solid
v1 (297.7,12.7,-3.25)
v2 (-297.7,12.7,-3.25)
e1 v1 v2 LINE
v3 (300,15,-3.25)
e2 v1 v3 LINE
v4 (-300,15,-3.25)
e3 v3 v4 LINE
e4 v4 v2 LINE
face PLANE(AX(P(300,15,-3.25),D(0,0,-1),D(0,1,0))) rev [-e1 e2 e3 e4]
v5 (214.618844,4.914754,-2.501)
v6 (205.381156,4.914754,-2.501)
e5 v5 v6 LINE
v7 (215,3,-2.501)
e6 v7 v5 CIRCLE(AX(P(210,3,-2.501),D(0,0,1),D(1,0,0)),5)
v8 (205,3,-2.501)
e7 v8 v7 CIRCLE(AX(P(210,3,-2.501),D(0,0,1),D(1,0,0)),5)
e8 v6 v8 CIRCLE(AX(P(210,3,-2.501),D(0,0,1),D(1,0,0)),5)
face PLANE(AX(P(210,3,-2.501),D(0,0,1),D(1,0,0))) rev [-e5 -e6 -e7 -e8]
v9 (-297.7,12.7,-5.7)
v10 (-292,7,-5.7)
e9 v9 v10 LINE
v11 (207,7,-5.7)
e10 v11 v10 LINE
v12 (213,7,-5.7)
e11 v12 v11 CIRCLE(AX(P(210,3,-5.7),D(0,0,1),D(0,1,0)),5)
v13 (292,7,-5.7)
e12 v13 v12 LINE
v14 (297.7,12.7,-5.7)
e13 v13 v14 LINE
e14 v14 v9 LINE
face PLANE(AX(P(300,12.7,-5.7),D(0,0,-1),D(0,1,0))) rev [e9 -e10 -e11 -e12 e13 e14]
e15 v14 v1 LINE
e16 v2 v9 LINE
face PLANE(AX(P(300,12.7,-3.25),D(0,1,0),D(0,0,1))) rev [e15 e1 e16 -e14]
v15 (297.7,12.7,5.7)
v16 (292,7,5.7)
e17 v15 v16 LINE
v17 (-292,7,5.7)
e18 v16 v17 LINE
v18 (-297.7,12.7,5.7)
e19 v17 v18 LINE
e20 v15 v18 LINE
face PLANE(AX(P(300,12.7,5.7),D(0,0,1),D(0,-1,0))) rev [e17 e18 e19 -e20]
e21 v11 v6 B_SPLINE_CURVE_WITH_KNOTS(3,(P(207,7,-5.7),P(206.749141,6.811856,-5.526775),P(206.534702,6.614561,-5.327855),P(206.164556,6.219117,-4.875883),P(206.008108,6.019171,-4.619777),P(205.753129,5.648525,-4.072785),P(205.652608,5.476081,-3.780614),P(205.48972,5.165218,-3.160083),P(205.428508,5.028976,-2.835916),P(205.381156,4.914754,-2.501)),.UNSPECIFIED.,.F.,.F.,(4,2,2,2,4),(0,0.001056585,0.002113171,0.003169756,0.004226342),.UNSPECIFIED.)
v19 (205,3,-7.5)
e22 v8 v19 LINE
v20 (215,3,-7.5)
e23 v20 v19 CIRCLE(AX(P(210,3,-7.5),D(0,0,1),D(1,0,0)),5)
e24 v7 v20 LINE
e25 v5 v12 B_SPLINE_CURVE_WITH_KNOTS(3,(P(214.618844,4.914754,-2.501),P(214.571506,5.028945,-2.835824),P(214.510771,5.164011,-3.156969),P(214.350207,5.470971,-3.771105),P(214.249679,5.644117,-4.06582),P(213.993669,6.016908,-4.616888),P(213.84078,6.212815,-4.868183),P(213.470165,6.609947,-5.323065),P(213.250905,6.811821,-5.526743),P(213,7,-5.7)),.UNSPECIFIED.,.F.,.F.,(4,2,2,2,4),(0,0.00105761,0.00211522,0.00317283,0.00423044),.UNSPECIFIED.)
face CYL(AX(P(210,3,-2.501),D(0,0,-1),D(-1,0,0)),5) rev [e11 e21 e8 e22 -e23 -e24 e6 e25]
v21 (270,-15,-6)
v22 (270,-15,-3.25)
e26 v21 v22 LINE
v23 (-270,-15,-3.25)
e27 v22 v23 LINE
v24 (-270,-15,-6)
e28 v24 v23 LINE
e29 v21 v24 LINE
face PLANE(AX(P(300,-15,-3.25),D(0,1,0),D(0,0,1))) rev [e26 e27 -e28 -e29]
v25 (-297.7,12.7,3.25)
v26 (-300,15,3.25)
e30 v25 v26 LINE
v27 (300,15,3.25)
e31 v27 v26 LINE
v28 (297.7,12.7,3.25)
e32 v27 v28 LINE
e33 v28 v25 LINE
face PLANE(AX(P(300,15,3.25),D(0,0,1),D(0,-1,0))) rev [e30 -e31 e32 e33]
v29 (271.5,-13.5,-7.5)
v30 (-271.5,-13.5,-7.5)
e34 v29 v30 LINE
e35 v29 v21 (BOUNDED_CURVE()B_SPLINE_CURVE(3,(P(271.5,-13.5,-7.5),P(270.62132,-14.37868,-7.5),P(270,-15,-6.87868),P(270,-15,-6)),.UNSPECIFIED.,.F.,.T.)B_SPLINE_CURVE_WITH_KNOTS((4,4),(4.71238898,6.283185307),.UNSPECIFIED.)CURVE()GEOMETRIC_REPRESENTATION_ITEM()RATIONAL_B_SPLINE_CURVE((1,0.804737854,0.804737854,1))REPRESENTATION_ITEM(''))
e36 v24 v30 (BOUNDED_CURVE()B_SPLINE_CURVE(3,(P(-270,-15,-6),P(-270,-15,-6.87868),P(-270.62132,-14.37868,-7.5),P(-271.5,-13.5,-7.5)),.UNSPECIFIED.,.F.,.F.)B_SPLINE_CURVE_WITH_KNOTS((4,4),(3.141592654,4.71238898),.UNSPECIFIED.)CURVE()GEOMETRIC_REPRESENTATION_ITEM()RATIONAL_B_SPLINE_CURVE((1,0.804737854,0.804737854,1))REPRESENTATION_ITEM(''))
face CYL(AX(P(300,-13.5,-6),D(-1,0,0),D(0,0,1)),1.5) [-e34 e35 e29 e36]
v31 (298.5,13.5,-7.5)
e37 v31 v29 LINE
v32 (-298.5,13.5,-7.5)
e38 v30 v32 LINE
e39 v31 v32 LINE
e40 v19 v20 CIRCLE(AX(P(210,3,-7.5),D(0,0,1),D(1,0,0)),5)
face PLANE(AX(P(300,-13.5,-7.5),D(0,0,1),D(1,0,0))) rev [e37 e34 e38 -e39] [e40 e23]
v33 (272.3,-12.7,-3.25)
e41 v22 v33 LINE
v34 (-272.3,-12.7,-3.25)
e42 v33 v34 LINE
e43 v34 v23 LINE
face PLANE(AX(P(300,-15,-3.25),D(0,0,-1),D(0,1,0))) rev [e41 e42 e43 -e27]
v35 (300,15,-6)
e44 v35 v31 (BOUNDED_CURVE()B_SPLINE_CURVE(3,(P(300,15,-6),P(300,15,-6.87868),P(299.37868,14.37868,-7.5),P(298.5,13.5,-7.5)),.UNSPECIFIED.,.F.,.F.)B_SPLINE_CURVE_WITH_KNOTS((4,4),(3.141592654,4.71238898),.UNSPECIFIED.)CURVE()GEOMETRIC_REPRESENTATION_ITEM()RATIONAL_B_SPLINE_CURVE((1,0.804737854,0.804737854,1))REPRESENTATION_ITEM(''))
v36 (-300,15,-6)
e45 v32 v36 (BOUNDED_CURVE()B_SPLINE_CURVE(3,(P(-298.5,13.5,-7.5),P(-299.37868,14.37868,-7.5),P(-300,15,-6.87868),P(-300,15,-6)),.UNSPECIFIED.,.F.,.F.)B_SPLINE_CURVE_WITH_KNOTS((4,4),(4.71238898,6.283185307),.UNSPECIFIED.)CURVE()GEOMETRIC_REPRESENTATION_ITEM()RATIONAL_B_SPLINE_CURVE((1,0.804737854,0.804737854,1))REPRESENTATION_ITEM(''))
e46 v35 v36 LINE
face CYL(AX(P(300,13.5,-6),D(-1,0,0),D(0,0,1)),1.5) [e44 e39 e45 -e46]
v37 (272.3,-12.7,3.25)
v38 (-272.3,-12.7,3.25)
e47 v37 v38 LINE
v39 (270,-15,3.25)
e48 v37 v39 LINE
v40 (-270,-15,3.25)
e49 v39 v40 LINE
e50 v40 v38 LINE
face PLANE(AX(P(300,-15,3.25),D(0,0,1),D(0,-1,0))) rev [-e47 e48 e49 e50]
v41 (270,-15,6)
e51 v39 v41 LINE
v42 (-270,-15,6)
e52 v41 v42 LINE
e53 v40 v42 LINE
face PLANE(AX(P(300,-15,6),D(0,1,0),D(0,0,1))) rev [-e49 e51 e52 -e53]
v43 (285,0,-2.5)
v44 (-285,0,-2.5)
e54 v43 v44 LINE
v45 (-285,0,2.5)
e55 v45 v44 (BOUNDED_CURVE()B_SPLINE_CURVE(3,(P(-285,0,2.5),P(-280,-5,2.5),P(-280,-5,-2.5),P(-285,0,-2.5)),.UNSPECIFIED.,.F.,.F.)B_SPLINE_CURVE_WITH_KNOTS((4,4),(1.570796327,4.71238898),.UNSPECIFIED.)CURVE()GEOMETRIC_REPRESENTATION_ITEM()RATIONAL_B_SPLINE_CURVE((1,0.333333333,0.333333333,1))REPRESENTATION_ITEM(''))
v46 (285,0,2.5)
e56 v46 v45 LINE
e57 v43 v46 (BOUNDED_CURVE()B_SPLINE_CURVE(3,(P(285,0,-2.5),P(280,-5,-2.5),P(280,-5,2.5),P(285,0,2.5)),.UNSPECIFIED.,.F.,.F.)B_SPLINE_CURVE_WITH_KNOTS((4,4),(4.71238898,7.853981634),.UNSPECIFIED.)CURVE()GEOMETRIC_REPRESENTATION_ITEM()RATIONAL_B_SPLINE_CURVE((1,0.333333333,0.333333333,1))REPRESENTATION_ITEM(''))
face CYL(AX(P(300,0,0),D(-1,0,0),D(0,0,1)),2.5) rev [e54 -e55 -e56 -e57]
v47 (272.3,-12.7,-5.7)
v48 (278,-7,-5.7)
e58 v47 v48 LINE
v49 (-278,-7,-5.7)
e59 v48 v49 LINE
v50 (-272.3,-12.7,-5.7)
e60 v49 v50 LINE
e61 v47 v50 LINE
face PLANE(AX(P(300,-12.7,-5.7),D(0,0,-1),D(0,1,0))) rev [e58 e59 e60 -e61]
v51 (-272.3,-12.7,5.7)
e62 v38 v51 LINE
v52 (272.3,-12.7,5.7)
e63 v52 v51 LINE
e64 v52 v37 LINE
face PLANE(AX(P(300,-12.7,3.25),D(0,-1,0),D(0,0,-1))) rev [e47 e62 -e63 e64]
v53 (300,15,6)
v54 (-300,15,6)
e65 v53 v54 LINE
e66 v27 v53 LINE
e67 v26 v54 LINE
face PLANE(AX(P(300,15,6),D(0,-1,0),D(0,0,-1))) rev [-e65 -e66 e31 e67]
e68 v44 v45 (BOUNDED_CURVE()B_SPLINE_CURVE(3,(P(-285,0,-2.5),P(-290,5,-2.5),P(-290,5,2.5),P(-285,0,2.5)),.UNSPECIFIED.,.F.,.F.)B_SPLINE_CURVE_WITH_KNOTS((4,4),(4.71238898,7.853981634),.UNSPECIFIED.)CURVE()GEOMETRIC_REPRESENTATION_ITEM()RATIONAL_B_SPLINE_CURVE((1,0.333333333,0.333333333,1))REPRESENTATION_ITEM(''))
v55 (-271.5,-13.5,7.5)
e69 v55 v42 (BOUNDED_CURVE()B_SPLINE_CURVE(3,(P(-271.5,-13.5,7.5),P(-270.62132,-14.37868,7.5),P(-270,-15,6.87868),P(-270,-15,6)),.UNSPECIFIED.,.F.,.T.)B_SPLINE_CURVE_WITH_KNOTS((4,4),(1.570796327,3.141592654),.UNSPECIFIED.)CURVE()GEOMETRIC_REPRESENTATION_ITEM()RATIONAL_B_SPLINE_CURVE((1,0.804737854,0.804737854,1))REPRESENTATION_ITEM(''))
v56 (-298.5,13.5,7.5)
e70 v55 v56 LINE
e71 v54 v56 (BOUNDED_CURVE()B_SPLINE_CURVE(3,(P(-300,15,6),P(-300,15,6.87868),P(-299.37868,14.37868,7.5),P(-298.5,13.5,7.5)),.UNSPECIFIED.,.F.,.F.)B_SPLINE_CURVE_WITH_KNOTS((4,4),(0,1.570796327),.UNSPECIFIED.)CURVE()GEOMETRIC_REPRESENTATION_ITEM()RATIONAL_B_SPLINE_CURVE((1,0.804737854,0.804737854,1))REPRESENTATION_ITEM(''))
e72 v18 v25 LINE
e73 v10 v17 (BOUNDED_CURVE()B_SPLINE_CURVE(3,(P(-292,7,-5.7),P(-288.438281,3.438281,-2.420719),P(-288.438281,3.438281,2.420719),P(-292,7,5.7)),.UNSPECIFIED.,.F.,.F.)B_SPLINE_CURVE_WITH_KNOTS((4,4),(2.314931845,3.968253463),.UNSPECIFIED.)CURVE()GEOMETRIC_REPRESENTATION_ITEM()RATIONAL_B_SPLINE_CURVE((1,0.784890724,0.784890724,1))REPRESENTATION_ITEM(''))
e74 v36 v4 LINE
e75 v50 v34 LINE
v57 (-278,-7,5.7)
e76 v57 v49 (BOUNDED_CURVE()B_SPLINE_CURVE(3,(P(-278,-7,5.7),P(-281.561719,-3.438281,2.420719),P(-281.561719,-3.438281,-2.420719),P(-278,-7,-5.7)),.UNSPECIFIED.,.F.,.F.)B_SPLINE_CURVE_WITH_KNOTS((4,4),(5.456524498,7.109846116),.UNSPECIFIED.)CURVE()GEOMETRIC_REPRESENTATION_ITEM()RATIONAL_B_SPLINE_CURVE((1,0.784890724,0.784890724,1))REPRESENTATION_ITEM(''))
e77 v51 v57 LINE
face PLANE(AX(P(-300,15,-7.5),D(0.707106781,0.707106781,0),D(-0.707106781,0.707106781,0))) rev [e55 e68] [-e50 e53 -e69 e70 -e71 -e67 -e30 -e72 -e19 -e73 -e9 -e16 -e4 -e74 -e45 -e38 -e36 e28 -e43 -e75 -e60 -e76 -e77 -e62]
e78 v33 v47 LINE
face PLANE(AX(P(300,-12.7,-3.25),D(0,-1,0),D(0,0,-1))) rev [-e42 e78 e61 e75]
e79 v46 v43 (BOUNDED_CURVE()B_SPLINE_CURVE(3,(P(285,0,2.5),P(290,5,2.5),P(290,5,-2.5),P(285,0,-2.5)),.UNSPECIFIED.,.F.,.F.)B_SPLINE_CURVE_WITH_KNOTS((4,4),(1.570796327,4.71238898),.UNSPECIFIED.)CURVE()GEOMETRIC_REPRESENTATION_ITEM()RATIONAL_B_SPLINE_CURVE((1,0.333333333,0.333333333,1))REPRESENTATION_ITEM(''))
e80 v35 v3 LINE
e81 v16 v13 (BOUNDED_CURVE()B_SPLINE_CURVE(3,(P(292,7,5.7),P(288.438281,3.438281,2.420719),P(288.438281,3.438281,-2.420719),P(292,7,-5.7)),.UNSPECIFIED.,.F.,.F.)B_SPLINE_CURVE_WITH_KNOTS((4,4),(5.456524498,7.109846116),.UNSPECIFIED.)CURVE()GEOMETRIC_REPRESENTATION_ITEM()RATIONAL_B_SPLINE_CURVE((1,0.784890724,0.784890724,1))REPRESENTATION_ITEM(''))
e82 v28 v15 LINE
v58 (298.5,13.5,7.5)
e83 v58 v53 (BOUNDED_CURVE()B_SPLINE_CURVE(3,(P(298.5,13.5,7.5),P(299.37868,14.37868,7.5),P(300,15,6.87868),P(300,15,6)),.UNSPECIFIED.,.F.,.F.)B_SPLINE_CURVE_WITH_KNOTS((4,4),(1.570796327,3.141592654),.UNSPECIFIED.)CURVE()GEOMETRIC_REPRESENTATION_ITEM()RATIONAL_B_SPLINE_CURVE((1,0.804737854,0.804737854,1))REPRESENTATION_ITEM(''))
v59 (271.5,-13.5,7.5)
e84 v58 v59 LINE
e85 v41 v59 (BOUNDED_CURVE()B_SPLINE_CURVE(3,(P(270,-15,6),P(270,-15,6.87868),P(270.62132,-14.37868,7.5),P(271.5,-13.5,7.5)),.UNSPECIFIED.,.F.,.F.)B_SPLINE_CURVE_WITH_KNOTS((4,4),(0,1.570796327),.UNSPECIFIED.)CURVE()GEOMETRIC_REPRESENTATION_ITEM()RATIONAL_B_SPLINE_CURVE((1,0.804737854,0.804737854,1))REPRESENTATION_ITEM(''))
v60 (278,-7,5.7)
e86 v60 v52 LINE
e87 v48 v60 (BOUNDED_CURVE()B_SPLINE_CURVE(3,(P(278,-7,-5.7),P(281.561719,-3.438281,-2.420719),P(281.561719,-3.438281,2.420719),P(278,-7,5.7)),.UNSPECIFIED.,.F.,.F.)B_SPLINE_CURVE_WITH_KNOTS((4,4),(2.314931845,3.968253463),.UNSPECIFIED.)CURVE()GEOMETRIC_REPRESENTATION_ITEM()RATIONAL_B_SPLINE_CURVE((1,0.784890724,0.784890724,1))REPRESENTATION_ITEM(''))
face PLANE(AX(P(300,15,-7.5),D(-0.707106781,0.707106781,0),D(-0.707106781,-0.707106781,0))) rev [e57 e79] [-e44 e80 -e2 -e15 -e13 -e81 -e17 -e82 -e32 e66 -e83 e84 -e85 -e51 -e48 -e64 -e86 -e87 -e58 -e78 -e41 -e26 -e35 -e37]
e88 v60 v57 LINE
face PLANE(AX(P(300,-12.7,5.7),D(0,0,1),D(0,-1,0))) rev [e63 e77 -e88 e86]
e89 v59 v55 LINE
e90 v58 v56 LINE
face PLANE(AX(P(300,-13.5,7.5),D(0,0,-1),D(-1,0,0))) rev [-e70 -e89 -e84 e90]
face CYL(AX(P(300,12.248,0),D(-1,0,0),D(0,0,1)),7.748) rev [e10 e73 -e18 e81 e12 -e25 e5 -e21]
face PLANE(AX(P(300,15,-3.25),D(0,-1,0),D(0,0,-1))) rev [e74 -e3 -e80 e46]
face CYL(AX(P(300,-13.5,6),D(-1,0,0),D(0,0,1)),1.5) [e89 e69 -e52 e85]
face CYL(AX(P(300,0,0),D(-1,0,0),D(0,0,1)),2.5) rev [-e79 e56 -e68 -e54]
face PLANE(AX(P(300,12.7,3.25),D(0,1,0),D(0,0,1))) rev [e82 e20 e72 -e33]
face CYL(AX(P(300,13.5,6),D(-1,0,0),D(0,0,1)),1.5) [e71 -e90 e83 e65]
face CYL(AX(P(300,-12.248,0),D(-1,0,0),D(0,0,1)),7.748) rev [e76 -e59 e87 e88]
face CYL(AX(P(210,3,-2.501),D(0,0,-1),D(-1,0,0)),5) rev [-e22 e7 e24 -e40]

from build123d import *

# Parameters (mm, degrees)
SKETCH12_R          = 2.5
MEMBER_1_DEPTH      = 600
CUT_EXTRUDE_1_DEPTH = 301.749064836
SKETCH_7_R          = 5
CUT_EXTRUDE_2_DEPTH = 4.999


with BuildPart() as part:
    # Sketch12 → Member 1 (new body)
    with BuildSketch(Plane(origin=(-300, 0, 0), x_dir=(0, 0, -1), z_dir=(1, 0, 0))):
        with BuildLine():
            Line((-6, -15), (-3.25, -15))
            Line((-3.25, -15), (-3.25, -12.7))
            Line((-3.25, -12.7), (-5.7, -12.7))
            Line((-5.7, -12.7), (-5.7, -7))
            ThreePointArc((-5.7, -7), (0, -4.5), (5.7, -7))
            Line((5.7, -7), (5.7, -12.7))
            Line((5.7, -12.7), (3.25, -12.7))
            Line((3.25, -12.7), (3.25, -15))
            Line((3.25, -15), (6, -15))
            ThreePointArc((6, -15), (7.060660172, -14.560660172), (7.5, -13.5))
            Line((7.5, -13.5), (7.5, 13.5))
            ThreePointArc((7.5, 13.5), (7.060660172, 14.560660172), (6, 15))
            Line((6, 15), (3.25, 15))
            Line((3.25, 15), (3.25, 12.7))
            Line((3.25, 12.7), (5.7, 12.7))
            Line((5.7, 12.7), (5.7, 7))
            ThreePointArc((5.7, 7), (0, 4.5), (-5.7, 7))
            Line((-5.7, 7), (-5.7, 12.7))
            Line((-5.7, 12.7), (-3.25, 12.7))
            Line((-3.25, 12.7), (-3.25, 15))
            Line((-3.25, 15), (-6, 15))
            ThreePointArc((-6, 15), (-7.060660172, 14.560660172), (-7.5, 13.5))
            Line((-7.5, 13.5), (-7.5, -13.5))
            ThreePointArc((-7.5, -13.5), (-7.060660172, -14.560660172), (-6, -15))
        make_face()
        Circle(SKETCH12_R, mode=Mode.SUBTRACT)
    extrude(amount=MEMBER_1_DEPTH)

    # 草图4 → 切除-拉伸1 (cut, through all)
    with BuildSketch(Plane.XY.offset(7.5)):
        Polygon((-300, 15), (-270, -15), (-300, -15), align=None)
        Polygon((300, -15), (300, 15), (270, -15), align=None)
    extrude(amount=-CUT_EXTRUDE_1_DEPTH, mode=Mode.SUBTRACT)

    # 草图7 → 切除-拉伸2 (cut)
    with BuildSketch(Plane.XY.offset(-7.5)):
        with Locations(Location((210, 3, 0), (0, 0, 157.483422962))):
            Circle(SKETCH_7_R)
    extrude(amount=CUT_EXTRUDE_2_DEPTH, mode=Mode.SUBTRACT)


solid = part.part
